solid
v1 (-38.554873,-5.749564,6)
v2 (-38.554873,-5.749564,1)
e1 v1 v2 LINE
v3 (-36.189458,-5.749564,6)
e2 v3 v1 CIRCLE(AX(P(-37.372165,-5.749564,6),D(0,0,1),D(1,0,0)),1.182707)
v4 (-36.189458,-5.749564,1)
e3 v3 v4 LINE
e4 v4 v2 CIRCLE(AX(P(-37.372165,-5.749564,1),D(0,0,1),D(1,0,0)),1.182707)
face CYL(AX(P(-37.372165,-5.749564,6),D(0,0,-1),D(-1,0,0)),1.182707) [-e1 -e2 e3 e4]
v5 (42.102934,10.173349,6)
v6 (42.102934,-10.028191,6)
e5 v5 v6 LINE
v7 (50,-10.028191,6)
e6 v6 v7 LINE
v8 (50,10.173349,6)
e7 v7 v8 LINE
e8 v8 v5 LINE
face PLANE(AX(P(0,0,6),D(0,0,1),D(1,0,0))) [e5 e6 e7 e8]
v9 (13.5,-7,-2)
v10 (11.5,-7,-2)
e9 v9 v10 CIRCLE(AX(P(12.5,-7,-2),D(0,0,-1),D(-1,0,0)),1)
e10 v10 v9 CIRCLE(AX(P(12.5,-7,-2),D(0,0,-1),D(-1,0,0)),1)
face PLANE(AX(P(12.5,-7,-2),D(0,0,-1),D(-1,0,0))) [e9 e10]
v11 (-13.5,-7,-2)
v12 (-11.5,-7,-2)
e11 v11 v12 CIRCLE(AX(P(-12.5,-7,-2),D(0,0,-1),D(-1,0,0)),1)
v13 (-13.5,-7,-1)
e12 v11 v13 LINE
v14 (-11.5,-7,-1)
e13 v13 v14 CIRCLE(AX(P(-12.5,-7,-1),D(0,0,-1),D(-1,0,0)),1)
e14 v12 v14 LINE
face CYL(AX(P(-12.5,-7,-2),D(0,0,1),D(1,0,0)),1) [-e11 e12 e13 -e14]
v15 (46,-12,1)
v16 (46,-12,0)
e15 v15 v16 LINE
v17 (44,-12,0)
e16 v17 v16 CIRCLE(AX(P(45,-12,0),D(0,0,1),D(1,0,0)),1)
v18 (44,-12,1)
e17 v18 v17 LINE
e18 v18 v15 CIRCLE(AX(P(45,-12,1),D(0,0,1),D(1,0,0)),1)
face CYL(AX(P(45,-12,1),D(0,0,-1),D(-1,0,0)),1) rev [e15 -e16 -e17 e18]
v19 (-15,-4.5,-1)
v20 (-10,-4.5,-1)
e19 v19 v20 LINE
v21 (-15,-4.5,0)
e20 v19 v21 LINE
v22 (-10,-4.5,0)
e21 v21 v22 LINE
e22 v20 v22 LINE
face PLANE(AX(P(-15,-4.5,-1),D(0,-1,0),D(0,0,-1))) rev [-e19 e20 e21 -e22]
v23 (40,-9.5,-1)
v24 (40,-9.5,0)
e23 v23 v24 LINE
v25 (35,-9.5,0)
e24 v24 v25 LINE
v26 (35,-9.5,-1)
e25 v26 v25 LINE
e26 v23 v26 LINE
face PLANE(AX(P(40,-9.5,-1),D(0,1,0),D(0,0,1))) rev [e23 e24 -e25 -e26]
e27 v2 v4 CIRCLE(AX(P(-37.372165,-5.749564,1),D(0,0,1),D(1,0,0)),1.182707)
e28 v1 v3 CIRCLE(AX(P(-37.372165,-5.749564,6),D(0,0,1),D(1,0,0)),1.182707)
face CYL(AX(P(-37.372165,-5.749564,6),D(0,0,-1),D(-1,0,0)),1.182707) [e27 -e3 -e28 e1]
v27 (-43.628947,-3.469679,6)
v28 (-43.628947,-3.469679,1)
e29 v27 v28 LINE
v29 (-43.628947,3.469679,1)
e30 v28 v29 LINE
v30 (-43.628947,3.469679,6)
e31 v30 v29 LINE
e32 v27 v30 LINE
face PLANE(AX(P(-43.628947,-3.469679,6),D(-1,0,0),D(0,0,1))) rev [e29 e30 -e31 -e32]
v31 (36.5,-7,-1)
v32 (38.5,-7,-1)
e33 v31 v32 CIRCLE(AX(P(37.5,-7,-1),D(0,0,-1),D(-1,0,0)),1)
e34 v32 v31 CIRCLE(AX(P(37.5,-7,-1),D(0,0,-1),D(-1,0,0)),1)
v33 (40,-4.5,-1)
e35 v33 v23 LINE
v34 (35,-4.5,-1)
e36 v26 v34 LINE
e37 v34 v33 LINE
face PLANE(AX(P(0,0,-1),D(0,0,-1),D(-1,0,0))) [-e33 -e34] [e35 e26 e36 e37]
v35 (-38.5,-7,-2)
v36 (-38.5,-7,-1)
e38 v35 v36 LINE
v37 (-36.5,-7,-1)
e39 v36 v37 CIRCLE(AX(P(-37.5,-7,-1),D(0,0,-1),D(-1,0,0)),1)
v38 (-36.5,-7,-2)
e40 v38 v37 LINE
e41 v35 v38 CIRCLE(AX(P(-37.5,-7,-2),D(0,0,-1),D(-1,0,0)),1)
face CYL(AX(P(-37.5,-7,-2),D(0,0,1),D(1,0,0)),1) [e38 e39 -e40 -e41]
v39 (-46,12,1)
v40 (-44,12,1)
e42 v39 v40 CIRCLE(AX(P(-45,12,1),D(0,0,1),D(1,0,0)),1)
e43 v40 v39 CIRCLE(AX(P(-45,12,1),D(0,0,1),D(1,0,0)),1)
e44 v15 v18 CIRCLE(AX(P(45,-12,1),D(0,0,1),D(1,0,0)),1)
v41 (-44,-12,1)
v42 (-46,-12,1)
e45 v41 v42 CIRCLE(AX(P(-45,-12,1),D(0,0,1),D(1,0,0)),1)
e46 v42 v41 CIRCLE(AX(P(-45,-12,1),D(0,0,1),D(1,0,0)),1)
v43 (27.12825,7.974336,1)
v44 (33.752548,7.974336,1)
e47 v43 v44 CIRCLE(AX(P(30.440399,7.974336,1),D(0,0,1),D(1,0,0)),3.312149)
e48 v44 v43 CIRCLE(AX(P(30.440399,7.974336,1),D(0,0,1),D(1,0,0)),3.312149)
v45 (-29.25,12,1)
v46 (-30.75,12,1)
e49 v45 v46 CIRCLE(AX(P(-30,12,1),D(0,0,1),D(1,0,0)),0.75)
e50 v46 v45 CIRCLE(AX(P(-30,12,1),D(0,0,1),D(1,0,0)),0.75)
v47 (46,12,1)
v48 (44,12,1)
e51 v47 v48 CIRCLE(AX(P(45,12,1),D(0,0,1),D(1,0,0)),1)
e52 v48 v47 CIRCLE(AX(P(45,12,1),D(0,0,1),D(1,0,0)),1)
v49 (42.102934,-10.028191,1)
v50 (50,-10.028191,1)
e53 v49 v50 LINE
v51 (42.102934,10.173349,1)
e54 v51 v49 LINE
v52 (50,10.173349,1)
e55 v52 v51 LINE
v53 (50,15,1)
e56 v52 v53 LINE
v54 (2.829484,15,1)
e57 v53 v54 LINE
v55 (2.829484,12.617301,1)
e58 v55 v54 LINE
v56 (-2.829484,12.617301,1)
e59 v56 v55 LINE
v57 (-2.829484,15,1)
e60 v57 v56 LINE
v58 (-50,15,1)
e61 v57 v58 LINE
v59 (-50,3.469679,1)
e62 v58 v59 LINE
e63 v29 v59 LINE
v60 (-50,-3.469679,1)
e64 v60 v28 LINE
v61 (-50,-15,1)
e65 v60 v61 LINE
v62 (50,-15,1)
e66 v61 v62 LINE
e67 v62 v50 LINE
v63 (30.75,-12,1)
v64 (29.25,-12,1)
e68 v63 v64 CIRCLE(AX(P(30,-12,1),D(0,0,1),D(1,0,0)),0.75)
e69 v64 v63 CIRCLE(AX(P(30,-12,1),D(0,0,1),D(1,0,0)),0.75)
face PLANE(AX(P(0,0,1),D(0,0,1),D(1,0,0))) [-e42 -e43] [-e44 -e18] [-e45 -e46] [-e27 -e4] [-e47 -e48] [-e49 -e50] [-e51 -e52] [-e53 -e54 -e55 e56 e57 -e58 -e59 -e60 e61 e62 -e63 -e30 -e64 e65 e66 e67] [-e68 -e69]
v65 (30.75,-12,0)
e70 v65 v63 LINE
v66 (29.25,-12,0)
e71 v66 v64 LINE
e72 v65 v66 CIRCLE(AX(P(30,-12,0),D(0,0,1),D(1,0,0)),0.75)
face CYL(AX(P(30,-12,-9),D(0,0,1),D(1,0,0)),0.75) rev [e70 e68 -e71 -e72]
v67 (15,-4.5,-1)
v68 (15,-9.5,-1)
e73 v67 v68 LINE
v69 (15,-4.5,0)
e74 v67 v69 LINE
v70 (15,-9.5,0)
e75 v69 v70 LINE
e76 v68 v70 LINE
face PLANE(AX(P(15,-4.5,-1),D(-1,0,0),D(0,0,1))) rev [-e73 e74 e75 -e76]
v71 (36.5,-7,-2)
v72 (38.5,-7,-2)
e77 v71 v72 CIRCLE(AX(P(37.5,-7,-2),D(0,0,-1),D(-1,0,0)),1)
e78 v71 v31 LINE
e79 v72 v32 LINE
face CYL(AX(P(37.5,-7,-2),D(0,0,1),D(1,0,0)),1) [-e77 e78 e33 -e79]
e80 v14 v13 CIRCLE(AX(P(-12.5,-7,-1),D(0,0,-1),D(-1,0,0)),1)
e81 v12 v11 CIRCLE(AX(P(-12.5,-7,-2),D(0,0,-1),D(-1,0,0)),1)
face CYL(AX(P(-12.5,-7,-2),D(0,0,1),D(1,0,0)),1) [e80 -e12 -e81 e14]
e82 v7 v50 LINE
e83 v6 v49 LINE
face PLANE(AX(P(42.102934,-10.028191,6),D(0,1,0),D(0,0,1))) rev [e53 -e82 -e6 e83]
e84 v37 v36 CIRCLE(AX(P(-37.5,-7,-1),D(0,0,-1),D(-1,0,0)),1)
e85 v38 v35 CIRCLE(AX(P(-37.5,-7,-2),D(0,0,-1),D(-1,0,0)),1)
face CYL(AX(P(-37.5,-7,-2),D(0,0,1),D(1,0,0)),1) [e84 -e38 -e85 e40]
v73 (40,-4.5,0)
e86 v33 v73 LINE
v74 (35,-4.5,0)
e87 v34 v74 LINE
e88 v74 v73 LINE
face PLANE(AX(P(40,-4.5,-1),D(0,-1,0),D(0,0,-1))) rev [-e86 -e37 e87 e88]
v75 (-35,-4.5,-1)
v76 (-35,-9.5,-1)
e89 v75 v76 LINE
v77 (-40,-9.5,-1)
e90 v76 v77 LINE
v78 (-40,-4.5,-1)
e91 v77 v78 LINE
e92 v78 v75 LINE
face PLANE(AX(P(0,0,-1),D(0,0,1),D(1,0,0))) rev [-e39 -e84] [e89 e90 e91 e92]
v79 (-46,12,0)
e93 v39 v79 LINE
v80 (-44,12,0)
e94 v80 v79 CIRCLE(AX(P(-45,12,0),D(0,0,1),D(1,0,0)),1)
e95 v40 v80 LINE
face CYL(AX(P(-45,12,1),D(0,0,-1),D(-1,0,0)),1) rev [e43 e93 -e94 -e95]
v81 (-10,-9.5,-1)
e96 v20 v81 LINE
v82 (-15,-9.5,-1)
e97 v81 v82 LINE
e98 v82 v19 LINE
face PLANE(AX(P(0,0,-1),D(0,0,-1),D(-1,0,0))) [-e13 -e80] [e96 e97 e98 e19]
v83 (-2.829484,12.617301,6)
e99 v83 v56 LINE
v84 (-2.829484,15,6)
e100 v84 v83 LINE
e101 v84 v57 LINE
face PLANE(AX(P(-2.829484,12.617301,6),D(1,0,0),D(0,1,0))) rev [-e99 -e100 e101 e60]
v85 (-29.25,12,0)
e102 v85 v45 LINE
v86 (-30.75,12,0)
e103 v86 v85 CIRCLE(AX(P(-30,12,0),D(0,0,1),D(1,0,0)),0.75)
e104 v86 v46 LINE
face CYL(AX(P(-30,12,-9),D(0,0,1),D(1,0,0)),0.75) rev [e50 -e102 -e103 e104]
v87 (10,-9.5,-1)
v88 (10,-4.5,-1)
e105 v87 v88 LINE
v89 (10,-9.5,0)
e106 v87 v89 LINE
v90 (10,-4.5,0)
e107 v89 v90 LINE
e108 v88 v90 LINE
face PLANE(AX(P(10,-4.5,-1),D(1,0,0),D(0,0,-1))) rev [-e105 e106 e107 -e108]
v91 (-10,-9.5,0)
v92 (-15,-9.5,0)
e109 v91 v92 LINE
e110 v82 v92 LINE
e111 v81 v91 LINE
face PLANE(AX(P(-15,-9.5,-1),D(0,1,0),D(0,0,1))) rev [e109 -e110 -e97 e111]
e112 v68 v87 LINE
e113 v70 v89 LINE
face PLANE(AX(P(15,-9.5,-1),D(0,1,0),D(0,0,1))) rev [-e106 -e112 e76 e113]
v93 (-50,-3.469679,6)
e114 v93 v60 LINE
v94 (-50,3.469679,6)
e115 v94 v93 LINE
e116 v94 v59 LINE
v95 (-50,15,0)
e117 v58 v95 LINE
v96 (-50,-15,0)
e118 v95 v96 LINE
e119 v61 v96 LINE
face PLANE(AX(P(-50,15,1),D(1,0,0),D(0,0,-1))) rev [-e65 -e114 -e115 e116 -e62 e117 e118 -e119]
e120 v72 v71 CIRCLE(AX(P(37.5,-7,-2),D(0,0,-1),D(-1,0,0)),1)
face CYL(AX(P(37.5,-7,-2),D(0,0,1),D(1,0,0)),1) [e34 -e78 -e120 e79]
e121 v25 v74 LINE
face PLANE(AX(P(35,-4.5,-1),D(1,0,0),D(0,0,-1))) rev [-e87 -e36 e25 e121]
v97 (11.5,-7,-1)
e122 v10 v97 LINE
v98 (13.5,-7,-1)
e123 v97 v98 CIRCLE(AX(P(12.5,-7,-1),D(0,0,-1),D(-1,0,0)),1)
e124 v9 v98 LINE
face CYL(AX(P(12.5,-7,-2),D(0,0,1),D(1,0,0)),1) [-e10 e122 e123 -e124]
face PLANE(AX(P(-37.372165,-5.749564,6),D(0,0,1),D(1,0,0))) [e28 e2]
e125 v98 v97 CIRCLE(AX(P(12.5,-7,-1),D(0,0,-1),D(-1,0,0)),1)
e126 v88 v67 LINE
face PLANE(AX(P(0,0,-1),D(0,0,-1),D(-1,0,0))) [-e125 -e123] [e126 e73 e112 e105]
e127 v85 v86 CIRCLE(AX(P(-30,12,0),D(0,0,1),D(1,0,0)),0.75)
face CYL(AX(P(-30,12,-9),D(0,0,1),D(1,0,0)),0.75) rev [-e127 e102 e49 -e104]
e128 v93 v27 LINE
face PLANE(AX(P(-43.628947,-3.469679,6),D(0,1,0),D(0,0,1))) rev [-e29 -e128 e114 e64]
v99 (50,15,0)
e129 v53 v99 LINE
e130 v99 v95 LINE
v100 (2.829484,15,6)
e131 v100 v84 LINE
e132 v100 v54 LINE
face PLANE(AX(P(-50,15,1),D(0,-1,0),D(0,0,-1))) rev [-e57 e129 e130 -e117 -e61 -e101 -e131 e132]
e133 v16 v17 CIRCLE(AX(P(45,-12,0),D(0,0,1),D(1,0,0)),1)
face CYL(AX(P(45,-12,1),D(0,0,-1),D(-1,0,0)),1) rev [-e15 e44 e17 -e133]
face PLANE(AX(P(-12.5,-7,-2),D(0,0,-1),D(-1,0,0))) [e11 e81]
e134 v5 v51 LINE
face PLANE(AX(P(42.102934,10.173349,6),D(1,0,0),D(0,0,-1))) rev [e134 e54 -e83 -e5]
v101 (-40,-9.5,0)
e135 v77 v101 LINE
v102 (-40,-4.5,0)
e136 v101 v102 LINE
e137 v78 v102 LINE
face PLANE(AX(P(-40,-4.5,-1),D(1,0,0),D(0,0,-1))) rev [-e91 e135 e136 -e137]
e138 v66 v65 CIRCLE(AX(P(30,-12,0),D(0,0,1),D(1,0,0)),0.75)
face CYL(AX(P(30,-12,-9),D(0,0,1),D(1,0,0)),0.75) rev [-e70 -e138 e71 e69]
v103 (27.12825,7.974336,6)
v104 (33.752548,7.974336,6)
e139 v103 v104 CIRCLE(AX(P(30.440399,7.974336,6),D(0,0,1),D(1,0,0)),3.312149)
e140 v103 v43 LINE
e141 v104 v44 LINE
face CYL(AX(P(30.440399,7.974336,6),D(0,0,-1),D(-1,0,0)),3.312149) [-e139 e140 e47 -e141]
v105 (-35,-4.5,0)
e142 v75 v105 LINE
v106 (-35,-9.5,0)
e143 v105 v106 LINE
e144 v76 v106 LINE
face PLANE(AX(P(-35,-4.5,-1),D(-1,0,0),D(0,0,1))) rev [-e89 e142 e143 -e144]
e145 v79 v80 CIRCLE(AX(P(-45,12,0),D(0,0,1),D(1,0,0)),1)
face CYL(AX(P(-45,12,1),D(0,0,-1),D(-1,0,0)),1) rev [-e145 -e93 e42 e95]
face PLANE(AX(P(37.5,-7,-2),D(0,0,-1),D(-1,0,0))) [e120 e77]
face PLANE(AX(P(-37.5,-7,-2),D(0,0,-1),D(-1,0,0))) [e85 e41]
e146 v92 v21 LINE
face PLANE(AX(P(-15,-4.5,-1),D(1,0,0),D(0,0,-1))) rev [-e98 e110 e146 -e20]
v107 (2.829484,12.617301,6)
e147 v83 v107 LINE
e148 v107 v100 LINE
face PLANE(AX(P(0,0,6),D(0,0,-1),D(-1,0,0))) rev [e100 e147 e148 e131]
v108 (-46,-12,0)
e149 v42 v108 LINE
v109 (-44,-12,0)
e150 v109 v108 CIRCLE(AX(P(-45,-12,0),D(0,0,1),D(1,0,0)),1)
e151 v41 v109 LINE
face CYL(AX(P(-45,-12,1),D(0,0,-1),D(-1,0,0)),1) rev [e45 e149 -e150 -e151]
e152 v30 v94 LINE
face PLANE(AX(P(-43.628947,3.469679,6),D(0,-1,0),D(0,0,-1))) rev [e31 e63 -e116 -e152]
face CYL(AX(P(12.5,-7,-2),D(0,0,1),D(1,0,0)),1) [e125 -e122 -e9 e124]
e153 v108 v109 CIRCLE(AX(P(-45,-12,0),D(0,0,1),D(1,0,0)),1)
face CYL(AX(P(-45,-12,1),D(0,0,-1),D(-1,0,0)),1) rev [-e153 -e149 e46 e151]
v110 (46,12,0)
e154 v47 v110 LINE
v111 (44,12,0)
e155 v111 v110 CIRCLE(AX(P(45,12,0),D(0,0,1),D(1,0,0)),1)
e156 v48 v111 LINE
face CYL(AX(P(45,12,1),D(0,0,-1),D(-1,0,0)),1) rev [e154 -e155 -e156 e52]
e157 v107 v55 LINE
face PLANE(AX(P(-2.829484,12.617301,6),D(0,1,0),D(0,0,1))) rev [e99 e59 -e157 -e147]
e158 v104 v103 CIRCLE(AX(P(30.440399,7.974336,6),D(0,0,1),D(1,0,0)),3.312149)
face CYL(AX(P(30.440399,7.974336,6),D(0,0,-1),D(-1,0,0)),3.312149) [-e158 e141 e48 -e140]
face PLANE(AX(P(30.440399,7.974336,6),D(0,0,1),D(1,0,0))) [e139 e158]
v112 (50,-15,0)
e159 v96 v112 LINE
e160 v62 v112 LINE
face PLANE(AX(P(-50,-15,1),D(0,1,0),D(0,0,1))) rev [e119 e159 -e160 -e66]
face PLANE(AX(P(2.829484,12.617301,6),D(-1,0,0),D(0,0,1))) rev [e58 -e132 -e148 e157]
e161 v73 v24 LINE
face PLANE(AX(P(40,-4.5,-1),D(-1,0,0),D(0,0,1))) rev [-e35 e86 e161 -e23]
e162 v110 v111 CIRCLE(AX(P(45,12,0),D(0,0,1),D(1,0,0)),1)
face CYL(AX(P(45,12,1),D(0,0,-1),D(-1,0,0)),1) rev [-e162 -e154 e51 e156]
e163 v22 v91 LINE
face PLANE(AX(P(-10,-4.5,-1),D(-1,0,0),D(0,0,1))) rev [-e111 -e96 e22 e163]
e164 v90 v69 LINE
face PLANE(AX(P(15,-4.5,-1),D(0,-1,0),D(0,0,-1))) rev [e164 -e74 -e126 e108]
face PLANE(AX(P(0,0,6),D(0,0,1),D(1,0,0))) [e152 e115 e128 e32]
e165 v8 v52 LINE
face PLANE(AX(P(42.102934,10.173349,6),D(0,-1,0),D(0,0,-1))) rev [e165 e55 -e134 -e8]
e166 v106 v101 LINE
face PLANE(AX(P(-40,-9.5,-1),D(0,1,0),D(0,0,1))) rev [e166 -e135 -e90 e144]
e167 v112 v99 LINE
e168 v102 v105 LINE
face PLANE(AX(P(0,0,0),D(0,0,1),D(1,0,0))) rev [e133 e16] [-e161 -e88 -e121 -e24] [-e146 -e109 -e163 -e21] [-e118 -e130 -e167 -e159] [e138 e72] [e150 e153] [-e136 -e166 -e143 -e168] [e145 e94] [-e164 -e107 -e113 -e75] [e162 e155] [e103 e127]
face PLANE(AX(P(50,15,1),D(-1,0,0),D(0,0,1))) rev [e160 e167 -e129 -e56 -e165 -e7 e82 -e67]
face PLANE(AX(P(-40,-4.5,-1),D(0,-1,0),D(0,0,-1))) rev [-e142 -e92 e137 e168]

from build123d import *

# Parameters (mm, degrees)
SKETCH1_W           = 100
SKETCH1_H           = 30
SKETCH1_R           = 1
BOSS_EXTRUDE1_DEPTH = 1
SKETCH2_R           = 3.312148645
SKETCH2_R_2         = 1.182707094
SKETCH2_W           = 7.897065894
SKETCH2_H           = 20.201539664
SKETCH2_W_2         = 5.658967966
SKETCH2_H_2         = 2.382698796
SKETCH2_W_3         = 6.371052581
SKETCH2_H_3         = 6.939357654
BOSS_EXTRUDE2_DEPTH = 5
SKETCH3_W           = 5
SKETCH3_H           = 5
BOSS_EXTRUDE3_DEPTH = 1
SKETCH4_R           = 1
BOSS_EXTRUDE4_DEPTH = 1
SKETCH5_R           = 0.75
CUT_EXTRUDE1_DEPTH  = 10


with BuildPart() as part:
    # Sketch1 → Boss-Extrude1 (new body)
    with BuildSketch(Plane.XY):
        Rectangle(SKETCH1_W, SKETCH1_H)
        with Locations((-45, -12)):
            Circle(SKETCH1_R, mode=Mode.SUBTRACT)
        with Locations((-45, 12)):
            Circle(SKETCH1_R, mode=Mode.SUBTRACT)
        with Locations((45, 12)):
            Circle(SKETCH1_R, mode=Mode.SUBTRACT)
        with Locations((45, -12)):
            Circle(SKETCH1_R, mode=Mode.SUBTRACT)
    extrude(amount=BOSS_EXTRUDE1_DEPTH)

    # Sketch2 → Boss-Extrude2 (add)
    with BuildSketch(Plane.XY.offset(1)):
        with Locations((30.440398969, 7.974336126)):
            Circle(SKETCH2_R)
        with Locations((-37.372165455, -5.749563916)):
            Circle(SKETCH2_R_2)
        with Locations((46.051467053, 0.07257894)):
            Rectangle(SKETCH2_W, SKETCH2_H)
        with Locations((0, 13.808650602)):
            Rectangle(SKETCH2_W_2, SKETCH2_H_2)
        with Locations((-46.814473709, 0)):
            Rectangle(SKETCH2_W_3, SKETCH2_H_3)
    extrude(amount=BOSS_EXTRUDE2_DEPTH)

    # Sketch3 → Boss-Extrude3 (add)
    with BuildSketch(Plane(origin=(0, 0, 0), x_dir=(-1, 0, 0), z_dir=(0, 0, -1))):
        with Locations((-12.5, -7)):
            Rectangle(SKETCH3_W, SKETCH3_H)
        with Locations((-37.5, -7)):
            Rectangle(SKETCH3_W, SKETCH3_H)
        with Locations((37.5, -7)):
            Rectangle(SKETCH3_W, SKETCH3_H)
        with Locations((12.5, -7)):
            Rectangle(SKETCH3_W, SKETCH3_H)
    extrude(amount=BOSS_EXTRUDE3_DEPTH)

    # Sketch4 → Boss-Extrude4 (add)
    with BuildSketch(Plane(origin=(0, 0, -1), x_dir=(-1, 0, 0), z_dir=(0, 0, -1))):
        with Locations((-37.5, -7)):
            Circle(SKETCH4_R)
        with Locations((-12.5, -7)):
            Circle(SKETCH4_R)
        with Locations((12.5, -7)):
            Circle(SKETCH4_R)
        with Locations((37.5, -7)):
            Circle(SKETCH4_R)
    extrude(amount=BOSS_EXTRUDE4_DEPTH)

    # Sketch5 → Cut-Extrude1 (cut)
    with BuildSketch(Plane.XY.offset(1)):
        with Locations((30, -12)):
            Circle(SKETCH5_R)
        with Locations((-30, 12)):
            Circle(SKETCH5_R)
    extrude(amount=-CUT_EXTRUDE1_DEPTH, mode=Mode.SUBTRACT)


solid = part.part
